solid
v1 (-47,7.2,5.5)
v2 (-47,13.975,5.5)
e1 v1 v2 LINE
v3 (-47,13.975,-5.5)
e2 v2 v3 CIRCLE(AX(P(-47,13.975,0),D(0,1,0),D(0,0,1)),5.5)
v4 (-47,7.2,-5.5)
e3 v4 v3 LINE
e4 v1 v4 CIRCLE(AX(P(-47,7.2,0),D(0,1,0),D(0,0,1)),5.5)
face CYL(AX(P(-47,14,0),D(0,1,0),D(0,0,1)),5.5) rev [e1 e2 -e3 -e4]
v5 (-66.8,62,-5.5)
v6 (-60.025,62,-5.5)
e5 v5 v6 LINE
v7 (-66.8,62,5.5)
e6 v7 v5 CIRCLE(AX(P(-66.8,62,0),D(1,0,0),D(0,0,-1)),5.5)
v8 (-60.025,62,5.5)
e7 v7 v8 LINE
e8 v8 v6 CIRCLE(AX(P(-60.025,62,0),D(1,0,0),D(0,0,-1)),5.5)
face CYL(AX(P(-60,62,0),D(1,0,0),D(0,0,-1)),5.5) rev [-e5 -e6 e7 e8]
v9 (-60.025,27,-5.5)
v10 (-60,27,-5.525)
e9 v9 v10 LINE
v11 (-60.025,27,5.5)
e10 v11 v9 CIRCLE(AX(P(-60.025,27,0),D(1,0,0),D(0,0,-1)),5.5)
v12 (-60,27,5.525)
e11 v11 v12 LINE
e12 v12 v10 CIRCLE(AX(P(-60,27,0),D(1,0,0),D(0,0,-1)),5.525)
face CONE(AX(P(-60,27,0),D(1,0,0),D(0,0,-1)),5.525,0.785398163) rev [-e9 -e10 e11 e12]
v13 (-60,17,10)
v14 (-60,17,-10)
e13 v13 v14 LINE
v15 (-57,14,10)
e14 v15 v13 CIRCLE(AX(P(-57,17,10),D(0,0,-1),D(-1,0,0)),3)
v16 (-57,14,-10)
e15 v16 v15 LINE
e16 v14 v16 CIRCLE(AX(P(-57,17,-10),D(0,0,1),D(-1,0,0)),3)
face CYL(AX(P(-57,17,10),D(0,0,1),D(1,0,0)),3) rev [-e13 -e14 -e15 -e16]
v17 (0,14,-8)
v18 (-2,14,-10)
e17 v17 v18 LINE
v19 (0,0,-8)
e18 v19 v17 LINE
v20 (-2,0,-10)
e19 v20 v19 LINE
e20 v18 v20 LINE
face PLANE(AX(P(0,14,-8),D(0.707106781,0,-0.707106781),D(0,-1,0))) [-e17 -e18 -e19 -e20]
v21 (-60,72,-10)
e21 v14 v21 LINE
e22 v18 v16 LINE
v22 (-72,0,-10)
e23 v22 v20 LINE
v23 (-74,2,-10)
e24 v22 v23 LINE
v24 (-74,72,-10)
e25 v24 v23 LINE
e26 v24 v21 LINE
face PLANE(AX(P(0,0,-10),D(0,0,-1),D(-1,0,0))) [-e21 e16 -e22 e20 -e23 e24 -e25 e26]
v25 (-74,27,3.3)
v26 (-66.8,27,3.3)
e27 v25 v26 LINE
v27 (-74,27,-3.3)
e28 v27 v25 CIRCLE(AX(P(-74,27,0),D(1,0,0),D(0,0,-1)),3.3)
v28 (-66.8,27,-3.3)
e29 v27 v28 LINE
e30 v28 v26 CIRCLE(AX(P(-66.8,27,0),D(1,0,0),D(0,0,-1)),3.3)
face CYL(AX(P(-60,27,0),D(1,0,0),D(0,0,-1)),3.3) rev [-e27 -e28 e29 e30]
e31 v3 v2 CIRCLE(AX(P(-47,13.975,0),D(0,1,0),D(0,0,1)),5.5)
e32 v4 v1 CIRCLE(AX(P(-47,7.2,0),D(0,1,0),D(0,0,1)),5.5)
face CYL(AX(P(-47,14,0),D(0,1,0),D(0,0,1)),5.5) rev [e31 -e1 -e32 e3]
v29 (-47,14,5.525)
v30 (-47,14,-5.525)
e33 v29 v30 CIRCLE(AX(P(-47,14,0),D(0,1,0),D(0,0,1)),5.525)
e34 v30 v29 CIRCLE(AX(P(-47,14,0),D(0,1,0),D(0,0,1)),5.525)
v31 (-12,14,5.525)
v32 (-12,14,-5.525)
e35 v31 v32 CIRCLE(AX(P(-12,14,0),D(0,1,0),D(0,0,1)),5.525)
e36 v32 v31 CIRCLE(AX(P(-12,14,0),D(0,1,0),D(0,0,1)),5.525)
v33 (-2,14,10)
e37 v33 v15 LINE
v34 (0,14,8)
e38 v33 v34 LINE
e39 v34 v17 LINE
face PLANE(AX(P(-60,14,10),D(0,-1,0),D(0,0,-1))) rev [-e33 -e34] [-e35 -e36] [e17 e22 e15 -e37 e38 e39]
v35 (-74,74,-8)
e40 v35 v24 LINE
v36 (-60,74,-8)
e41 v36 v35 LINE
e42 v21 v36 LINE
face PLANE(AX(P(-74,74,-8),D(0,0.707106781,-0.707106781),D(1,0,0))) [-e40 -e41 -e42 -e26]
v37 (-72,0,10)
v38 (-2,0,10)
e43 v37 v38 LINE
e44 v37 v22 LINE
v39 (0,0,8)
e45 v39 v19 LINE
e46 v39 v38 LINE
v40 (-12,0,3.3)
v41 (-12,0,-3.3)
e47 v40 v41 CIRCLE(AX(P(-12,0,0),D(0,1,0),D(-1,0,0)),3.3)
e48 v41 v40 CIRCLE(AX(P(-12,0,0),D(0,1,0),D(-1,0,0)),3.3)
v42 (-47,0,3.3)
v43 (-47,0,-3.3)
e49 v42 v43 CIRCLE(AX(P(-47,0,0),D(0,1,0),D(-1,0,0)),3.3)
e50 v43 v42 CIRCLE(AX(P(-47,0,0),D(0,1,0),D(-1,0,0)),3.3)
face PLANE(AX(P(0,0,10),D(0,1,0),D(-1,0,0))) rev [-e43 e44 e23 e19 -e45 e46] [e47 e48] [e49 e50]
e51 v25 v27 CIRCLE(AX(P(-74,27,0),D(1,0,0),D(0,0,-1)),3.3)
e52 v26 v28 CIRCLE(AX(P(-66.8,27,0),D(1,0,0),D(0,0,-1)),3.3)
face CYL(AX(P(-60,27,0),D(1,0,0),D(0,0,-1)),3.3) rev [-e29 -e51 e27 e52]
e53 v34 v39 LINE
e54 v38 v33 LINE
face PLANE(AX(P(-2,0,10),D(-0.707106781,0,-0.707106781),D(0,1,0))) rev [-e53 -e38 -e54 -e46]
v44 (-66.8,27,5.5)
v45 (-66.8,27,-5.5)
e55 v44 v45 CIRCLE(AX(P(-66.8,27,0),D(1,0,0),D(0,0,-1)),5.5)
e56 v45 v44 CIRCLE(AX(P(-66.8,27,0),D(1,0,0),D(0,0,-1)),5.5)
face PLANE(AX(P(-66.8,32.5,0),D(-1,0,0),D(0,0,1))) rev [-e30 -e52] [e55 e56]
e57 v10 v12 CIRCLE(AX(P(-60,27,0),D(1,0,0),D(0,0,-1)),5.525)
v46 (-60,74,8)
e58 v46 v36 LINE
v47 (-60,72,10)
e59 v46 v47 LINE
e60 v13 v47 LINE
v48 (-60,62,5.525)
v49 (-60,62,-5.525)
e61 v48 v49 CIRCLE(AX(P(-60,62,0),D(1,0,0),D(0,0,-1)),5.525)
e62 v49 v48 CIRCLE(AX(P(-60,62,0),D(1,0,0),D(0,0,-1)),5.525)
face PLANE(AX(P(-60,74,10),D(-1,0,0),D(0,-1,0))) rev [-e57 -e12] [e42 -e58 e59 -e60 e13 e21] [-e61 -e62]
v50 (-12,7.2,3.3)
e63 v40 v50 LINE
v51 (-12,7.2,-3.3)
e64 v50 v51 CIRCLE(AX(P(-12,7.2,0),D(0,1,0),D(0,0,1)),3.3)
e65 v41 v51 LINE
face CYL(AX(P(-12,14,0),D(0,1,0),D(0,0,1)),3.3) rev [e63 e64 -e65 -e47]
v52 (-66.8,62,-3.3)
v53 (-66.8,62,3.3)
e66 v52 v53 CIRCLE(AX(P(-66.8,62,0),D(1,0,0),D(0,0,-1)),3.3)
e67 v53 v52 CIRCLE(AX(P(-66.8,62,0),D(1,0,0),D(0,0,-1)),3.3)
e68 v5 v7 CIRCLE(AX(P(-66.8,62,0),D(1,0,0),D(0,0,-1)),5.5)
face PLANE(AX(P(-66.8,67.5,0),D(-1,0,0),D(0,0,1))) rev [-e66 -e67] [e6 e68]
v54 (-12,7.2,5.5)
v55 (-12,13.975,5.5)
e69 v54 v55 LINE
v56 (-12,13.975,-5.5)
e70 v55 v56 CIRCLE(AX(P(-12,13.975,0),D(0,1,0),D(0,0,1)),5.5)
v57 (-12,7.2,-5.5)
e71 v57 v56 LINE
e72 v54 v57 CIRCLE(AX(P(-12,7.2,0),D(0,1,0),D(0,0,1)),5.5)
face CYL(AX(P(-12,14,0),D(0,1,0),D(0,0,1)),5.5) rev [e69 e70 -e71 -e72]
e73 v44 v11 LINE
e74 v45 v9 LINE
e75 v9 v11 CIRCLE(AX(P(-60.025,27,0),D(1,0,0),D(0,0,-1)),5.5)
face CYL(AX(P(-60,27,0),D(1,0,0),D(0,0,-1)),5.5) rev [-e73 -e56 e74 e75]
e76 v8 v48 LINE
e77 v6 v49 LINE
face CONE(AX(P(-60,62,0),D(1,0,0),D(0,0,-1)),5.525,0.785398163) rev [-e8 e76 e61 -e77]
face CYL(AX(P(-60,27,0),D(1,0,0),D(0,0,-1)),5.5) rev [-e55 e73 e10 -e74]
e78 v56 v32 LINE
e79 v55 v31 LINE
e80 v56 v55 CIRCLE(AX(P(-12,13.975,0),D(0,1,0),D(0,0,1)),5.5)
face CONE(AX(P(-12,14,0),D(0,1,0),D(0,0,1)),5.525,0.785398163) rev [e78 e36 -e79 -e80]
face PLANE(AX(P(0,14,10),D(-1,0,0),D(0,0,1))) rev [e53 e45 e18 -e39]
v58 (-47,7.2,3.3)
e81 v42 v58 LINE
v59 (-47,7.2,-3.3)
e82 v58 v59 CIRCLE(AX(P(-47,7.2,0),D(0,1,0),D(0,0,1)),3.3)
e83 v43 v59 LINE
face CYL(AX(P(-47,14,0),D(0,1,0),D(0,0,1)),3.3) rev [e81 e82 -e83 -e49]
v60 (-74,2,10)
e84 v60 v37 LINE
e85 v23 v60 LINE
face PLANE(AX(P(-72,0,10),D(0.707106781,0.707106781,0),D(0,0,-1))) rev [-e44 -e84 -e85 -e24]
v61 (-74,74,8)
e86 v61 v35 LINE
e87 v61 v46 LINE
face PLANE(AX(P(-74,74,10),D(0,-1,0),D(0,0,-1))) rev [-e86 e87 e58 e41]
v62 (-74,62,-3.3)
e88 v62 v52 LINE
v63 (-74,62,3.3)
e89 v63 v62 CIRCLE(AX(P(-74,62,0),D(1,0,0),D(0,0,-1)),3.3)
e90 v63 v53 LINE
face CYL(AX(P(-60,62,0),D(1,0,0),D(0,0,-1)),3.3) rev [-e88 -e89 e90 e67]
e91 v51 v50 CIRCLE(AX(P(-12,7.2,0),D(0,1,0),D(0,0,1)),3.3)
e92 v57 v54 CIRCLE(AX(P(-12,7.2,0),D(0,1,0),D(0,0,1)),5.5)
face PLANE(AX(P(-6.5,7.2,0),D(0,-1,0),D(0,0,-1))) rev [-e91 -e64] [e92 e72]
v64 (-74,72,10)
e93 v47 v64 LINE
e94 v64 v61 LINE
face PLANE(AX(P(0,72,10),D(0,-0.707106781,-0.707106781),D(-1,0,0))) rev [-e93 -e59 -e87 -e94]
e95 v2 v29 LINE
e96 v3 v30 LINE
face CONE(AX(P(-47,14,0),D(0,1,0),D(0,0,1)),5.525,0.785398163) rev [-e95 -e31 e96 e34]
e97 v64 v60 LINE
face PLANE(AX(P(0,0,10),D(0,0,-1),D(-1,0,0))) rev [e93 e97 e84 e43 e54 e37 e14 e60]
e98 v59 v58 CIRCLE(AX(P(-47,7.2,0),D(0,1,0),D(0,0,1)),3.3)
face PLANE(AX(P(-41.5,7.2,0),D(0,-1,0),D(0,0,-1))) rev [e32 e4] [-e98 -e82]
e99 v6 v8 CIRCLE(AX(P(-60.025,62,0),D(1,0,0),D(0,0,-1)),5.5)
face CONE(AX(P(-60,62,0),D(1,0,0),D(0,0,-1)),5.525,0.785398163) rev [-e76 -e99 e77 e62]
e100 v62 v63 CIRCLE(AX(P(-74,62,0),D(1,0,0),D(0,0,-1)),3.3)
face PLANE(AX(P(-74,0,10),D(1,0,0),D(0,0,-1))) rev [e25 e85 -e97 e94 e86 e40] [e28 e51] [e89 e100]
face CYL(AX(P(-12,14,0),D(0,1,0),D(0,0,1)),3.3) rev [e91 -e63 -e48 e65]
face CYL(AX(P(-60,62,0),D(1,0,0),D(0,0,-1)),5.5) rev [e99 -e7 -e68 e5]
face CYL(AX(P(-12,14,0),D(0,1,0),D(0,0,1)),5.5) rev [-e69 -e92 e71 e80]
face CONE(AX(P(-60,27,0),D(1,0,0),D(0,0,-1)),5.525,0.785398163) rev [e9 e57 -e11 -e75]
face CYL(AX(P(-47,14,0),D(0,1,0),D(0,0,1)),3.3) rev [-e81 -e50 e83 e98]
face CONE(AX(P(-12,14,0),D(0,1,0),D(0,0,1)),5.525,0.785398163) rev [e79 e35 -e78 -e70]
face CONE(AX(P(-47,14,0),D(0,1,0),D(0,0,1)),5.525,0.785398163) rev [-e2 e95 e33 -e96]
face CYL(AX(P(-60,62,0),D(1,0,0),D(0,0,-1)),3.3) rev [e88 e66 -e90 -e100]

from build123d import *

# Parameters (mm, degrees)
EXTRUDE_1_DEPTH          = 10
FILLET_1_R               = 3
CHAMFER_1_SIZE           = 2
CHAMFER_2_SIZE           = 2
HOLE_WIZARD_1_AT_2_COUNT = 2
HOLE_WIZARD_1_AT_2_PITCH = 35
HOLE_WIZARD_2_AT_2_COUNT = 2
HOLE_WIZARD_2_AT_2_PITCH = 35


with BuildPart() as part:
    # 草图1 → 凸台-拉伸1 (new, symmetric)
    with BuildSketch(Plane.XY):
        Polygon((0, 0), (-74, 0), (-74, 74), (-60, 74), (-60, 14), (0, 14), align=None)
    extrude(amount=EXTRUDE_1_DEPTH, both=True)

    # 圆角1
    fillet_1_edges = [part.edges().sort_by_distance(p)[0] for p in [
        (-60, 14, 0),
    ]]
    fillet(fillet_1_edges, radius=FILLET_1_R)

    # 倒角1
    chamfer_1_edges = [part.edges().sort_by_distance(p)[0] for p in [
        (-67, 74, 10),
        (0, 7, 10),
        (-67, 74, -10),
        (0, 7, -10),
    ]]
    chamfer(chamfer_1_edges, length=CHAMFER_1_SIZE)

    # 倒角2
    chamfer_2_edges = [part.edges().sort_by_distance(p)[0] for p in [
        (-74, 0, 0),
    ]]
    chamfer(chamfer_2_edges, length=CHAMFER_2_SIZE)

    # 草图2 → 打孔尺寸(%根据)内六角圆柱头螺钉的类型1 (revolve, cut)
    with BuildSketch(Plane(origin=(-60, 62, 0), x_dir=(0, 0, -1), z_dir=(0, 1, 0))):
        Polygon((0, 0), (0, 14), (3.3, 14), (3.3, 6.8), (5.5, 6.8), (5.5, 0.025), (5.525, 0), align=None)
    hole_wizard_1 = revolve(axis=Axis((-53.65, 62, 0), (-1, 0, 0)), mode=Mode.SUBTRACT)

    # 打孔尺寸(%根据)内六角圆柱头螺钉的类型1 at 2: 打孔尺寸(%根据)内六角圆柱头螺钉的类型1 ×2
    with Locations(*[(0, -i * HOLE_WIZARD_1_AT_2_PITCH, 0) for i in range(1, HOLE_WIZARD_1_AT_2_COUNT)]):
        add(hole_wizard_1, mode=Mode.SUBTRACT)

    # 草图4 → 打孔尺寸(%根据)内六角圆柱头螺钉的类型2 (revolve, cut)
    with BuildSketch(Plane(origin=(-12, 14, 0), x_dir=(0, 0, 1), z_dir=(1, 0, 0))):
        Polygon((0, 0), (0, 14), (3.3, 14), (3.3, 6.8), (5.5, 6.8), (5.5, 0.025), (5.525, 0), align=None)
    hole_wizard_2 = revolve(axis=Axis((-12, 20.35, 0), (0, -1, 0)), mode=Mode.SUBTRACT)

    # 打孔尺寸(%根据)内六角圆柱头螺钉的类型2 at 2: 打孔尺寸(%根据)内六角圆柱头螺钉的类型2 ×2
    with Locations(*[(-i * HOLE_WIZARD_2_AT_2_PITCH, 0, 0) for i in range(1, HOLE_WIZARD_2_AT_2_COUNT)]):
        add(hole_wizard_2, mode=Mode.SUBTRACT)


solid = part.part
